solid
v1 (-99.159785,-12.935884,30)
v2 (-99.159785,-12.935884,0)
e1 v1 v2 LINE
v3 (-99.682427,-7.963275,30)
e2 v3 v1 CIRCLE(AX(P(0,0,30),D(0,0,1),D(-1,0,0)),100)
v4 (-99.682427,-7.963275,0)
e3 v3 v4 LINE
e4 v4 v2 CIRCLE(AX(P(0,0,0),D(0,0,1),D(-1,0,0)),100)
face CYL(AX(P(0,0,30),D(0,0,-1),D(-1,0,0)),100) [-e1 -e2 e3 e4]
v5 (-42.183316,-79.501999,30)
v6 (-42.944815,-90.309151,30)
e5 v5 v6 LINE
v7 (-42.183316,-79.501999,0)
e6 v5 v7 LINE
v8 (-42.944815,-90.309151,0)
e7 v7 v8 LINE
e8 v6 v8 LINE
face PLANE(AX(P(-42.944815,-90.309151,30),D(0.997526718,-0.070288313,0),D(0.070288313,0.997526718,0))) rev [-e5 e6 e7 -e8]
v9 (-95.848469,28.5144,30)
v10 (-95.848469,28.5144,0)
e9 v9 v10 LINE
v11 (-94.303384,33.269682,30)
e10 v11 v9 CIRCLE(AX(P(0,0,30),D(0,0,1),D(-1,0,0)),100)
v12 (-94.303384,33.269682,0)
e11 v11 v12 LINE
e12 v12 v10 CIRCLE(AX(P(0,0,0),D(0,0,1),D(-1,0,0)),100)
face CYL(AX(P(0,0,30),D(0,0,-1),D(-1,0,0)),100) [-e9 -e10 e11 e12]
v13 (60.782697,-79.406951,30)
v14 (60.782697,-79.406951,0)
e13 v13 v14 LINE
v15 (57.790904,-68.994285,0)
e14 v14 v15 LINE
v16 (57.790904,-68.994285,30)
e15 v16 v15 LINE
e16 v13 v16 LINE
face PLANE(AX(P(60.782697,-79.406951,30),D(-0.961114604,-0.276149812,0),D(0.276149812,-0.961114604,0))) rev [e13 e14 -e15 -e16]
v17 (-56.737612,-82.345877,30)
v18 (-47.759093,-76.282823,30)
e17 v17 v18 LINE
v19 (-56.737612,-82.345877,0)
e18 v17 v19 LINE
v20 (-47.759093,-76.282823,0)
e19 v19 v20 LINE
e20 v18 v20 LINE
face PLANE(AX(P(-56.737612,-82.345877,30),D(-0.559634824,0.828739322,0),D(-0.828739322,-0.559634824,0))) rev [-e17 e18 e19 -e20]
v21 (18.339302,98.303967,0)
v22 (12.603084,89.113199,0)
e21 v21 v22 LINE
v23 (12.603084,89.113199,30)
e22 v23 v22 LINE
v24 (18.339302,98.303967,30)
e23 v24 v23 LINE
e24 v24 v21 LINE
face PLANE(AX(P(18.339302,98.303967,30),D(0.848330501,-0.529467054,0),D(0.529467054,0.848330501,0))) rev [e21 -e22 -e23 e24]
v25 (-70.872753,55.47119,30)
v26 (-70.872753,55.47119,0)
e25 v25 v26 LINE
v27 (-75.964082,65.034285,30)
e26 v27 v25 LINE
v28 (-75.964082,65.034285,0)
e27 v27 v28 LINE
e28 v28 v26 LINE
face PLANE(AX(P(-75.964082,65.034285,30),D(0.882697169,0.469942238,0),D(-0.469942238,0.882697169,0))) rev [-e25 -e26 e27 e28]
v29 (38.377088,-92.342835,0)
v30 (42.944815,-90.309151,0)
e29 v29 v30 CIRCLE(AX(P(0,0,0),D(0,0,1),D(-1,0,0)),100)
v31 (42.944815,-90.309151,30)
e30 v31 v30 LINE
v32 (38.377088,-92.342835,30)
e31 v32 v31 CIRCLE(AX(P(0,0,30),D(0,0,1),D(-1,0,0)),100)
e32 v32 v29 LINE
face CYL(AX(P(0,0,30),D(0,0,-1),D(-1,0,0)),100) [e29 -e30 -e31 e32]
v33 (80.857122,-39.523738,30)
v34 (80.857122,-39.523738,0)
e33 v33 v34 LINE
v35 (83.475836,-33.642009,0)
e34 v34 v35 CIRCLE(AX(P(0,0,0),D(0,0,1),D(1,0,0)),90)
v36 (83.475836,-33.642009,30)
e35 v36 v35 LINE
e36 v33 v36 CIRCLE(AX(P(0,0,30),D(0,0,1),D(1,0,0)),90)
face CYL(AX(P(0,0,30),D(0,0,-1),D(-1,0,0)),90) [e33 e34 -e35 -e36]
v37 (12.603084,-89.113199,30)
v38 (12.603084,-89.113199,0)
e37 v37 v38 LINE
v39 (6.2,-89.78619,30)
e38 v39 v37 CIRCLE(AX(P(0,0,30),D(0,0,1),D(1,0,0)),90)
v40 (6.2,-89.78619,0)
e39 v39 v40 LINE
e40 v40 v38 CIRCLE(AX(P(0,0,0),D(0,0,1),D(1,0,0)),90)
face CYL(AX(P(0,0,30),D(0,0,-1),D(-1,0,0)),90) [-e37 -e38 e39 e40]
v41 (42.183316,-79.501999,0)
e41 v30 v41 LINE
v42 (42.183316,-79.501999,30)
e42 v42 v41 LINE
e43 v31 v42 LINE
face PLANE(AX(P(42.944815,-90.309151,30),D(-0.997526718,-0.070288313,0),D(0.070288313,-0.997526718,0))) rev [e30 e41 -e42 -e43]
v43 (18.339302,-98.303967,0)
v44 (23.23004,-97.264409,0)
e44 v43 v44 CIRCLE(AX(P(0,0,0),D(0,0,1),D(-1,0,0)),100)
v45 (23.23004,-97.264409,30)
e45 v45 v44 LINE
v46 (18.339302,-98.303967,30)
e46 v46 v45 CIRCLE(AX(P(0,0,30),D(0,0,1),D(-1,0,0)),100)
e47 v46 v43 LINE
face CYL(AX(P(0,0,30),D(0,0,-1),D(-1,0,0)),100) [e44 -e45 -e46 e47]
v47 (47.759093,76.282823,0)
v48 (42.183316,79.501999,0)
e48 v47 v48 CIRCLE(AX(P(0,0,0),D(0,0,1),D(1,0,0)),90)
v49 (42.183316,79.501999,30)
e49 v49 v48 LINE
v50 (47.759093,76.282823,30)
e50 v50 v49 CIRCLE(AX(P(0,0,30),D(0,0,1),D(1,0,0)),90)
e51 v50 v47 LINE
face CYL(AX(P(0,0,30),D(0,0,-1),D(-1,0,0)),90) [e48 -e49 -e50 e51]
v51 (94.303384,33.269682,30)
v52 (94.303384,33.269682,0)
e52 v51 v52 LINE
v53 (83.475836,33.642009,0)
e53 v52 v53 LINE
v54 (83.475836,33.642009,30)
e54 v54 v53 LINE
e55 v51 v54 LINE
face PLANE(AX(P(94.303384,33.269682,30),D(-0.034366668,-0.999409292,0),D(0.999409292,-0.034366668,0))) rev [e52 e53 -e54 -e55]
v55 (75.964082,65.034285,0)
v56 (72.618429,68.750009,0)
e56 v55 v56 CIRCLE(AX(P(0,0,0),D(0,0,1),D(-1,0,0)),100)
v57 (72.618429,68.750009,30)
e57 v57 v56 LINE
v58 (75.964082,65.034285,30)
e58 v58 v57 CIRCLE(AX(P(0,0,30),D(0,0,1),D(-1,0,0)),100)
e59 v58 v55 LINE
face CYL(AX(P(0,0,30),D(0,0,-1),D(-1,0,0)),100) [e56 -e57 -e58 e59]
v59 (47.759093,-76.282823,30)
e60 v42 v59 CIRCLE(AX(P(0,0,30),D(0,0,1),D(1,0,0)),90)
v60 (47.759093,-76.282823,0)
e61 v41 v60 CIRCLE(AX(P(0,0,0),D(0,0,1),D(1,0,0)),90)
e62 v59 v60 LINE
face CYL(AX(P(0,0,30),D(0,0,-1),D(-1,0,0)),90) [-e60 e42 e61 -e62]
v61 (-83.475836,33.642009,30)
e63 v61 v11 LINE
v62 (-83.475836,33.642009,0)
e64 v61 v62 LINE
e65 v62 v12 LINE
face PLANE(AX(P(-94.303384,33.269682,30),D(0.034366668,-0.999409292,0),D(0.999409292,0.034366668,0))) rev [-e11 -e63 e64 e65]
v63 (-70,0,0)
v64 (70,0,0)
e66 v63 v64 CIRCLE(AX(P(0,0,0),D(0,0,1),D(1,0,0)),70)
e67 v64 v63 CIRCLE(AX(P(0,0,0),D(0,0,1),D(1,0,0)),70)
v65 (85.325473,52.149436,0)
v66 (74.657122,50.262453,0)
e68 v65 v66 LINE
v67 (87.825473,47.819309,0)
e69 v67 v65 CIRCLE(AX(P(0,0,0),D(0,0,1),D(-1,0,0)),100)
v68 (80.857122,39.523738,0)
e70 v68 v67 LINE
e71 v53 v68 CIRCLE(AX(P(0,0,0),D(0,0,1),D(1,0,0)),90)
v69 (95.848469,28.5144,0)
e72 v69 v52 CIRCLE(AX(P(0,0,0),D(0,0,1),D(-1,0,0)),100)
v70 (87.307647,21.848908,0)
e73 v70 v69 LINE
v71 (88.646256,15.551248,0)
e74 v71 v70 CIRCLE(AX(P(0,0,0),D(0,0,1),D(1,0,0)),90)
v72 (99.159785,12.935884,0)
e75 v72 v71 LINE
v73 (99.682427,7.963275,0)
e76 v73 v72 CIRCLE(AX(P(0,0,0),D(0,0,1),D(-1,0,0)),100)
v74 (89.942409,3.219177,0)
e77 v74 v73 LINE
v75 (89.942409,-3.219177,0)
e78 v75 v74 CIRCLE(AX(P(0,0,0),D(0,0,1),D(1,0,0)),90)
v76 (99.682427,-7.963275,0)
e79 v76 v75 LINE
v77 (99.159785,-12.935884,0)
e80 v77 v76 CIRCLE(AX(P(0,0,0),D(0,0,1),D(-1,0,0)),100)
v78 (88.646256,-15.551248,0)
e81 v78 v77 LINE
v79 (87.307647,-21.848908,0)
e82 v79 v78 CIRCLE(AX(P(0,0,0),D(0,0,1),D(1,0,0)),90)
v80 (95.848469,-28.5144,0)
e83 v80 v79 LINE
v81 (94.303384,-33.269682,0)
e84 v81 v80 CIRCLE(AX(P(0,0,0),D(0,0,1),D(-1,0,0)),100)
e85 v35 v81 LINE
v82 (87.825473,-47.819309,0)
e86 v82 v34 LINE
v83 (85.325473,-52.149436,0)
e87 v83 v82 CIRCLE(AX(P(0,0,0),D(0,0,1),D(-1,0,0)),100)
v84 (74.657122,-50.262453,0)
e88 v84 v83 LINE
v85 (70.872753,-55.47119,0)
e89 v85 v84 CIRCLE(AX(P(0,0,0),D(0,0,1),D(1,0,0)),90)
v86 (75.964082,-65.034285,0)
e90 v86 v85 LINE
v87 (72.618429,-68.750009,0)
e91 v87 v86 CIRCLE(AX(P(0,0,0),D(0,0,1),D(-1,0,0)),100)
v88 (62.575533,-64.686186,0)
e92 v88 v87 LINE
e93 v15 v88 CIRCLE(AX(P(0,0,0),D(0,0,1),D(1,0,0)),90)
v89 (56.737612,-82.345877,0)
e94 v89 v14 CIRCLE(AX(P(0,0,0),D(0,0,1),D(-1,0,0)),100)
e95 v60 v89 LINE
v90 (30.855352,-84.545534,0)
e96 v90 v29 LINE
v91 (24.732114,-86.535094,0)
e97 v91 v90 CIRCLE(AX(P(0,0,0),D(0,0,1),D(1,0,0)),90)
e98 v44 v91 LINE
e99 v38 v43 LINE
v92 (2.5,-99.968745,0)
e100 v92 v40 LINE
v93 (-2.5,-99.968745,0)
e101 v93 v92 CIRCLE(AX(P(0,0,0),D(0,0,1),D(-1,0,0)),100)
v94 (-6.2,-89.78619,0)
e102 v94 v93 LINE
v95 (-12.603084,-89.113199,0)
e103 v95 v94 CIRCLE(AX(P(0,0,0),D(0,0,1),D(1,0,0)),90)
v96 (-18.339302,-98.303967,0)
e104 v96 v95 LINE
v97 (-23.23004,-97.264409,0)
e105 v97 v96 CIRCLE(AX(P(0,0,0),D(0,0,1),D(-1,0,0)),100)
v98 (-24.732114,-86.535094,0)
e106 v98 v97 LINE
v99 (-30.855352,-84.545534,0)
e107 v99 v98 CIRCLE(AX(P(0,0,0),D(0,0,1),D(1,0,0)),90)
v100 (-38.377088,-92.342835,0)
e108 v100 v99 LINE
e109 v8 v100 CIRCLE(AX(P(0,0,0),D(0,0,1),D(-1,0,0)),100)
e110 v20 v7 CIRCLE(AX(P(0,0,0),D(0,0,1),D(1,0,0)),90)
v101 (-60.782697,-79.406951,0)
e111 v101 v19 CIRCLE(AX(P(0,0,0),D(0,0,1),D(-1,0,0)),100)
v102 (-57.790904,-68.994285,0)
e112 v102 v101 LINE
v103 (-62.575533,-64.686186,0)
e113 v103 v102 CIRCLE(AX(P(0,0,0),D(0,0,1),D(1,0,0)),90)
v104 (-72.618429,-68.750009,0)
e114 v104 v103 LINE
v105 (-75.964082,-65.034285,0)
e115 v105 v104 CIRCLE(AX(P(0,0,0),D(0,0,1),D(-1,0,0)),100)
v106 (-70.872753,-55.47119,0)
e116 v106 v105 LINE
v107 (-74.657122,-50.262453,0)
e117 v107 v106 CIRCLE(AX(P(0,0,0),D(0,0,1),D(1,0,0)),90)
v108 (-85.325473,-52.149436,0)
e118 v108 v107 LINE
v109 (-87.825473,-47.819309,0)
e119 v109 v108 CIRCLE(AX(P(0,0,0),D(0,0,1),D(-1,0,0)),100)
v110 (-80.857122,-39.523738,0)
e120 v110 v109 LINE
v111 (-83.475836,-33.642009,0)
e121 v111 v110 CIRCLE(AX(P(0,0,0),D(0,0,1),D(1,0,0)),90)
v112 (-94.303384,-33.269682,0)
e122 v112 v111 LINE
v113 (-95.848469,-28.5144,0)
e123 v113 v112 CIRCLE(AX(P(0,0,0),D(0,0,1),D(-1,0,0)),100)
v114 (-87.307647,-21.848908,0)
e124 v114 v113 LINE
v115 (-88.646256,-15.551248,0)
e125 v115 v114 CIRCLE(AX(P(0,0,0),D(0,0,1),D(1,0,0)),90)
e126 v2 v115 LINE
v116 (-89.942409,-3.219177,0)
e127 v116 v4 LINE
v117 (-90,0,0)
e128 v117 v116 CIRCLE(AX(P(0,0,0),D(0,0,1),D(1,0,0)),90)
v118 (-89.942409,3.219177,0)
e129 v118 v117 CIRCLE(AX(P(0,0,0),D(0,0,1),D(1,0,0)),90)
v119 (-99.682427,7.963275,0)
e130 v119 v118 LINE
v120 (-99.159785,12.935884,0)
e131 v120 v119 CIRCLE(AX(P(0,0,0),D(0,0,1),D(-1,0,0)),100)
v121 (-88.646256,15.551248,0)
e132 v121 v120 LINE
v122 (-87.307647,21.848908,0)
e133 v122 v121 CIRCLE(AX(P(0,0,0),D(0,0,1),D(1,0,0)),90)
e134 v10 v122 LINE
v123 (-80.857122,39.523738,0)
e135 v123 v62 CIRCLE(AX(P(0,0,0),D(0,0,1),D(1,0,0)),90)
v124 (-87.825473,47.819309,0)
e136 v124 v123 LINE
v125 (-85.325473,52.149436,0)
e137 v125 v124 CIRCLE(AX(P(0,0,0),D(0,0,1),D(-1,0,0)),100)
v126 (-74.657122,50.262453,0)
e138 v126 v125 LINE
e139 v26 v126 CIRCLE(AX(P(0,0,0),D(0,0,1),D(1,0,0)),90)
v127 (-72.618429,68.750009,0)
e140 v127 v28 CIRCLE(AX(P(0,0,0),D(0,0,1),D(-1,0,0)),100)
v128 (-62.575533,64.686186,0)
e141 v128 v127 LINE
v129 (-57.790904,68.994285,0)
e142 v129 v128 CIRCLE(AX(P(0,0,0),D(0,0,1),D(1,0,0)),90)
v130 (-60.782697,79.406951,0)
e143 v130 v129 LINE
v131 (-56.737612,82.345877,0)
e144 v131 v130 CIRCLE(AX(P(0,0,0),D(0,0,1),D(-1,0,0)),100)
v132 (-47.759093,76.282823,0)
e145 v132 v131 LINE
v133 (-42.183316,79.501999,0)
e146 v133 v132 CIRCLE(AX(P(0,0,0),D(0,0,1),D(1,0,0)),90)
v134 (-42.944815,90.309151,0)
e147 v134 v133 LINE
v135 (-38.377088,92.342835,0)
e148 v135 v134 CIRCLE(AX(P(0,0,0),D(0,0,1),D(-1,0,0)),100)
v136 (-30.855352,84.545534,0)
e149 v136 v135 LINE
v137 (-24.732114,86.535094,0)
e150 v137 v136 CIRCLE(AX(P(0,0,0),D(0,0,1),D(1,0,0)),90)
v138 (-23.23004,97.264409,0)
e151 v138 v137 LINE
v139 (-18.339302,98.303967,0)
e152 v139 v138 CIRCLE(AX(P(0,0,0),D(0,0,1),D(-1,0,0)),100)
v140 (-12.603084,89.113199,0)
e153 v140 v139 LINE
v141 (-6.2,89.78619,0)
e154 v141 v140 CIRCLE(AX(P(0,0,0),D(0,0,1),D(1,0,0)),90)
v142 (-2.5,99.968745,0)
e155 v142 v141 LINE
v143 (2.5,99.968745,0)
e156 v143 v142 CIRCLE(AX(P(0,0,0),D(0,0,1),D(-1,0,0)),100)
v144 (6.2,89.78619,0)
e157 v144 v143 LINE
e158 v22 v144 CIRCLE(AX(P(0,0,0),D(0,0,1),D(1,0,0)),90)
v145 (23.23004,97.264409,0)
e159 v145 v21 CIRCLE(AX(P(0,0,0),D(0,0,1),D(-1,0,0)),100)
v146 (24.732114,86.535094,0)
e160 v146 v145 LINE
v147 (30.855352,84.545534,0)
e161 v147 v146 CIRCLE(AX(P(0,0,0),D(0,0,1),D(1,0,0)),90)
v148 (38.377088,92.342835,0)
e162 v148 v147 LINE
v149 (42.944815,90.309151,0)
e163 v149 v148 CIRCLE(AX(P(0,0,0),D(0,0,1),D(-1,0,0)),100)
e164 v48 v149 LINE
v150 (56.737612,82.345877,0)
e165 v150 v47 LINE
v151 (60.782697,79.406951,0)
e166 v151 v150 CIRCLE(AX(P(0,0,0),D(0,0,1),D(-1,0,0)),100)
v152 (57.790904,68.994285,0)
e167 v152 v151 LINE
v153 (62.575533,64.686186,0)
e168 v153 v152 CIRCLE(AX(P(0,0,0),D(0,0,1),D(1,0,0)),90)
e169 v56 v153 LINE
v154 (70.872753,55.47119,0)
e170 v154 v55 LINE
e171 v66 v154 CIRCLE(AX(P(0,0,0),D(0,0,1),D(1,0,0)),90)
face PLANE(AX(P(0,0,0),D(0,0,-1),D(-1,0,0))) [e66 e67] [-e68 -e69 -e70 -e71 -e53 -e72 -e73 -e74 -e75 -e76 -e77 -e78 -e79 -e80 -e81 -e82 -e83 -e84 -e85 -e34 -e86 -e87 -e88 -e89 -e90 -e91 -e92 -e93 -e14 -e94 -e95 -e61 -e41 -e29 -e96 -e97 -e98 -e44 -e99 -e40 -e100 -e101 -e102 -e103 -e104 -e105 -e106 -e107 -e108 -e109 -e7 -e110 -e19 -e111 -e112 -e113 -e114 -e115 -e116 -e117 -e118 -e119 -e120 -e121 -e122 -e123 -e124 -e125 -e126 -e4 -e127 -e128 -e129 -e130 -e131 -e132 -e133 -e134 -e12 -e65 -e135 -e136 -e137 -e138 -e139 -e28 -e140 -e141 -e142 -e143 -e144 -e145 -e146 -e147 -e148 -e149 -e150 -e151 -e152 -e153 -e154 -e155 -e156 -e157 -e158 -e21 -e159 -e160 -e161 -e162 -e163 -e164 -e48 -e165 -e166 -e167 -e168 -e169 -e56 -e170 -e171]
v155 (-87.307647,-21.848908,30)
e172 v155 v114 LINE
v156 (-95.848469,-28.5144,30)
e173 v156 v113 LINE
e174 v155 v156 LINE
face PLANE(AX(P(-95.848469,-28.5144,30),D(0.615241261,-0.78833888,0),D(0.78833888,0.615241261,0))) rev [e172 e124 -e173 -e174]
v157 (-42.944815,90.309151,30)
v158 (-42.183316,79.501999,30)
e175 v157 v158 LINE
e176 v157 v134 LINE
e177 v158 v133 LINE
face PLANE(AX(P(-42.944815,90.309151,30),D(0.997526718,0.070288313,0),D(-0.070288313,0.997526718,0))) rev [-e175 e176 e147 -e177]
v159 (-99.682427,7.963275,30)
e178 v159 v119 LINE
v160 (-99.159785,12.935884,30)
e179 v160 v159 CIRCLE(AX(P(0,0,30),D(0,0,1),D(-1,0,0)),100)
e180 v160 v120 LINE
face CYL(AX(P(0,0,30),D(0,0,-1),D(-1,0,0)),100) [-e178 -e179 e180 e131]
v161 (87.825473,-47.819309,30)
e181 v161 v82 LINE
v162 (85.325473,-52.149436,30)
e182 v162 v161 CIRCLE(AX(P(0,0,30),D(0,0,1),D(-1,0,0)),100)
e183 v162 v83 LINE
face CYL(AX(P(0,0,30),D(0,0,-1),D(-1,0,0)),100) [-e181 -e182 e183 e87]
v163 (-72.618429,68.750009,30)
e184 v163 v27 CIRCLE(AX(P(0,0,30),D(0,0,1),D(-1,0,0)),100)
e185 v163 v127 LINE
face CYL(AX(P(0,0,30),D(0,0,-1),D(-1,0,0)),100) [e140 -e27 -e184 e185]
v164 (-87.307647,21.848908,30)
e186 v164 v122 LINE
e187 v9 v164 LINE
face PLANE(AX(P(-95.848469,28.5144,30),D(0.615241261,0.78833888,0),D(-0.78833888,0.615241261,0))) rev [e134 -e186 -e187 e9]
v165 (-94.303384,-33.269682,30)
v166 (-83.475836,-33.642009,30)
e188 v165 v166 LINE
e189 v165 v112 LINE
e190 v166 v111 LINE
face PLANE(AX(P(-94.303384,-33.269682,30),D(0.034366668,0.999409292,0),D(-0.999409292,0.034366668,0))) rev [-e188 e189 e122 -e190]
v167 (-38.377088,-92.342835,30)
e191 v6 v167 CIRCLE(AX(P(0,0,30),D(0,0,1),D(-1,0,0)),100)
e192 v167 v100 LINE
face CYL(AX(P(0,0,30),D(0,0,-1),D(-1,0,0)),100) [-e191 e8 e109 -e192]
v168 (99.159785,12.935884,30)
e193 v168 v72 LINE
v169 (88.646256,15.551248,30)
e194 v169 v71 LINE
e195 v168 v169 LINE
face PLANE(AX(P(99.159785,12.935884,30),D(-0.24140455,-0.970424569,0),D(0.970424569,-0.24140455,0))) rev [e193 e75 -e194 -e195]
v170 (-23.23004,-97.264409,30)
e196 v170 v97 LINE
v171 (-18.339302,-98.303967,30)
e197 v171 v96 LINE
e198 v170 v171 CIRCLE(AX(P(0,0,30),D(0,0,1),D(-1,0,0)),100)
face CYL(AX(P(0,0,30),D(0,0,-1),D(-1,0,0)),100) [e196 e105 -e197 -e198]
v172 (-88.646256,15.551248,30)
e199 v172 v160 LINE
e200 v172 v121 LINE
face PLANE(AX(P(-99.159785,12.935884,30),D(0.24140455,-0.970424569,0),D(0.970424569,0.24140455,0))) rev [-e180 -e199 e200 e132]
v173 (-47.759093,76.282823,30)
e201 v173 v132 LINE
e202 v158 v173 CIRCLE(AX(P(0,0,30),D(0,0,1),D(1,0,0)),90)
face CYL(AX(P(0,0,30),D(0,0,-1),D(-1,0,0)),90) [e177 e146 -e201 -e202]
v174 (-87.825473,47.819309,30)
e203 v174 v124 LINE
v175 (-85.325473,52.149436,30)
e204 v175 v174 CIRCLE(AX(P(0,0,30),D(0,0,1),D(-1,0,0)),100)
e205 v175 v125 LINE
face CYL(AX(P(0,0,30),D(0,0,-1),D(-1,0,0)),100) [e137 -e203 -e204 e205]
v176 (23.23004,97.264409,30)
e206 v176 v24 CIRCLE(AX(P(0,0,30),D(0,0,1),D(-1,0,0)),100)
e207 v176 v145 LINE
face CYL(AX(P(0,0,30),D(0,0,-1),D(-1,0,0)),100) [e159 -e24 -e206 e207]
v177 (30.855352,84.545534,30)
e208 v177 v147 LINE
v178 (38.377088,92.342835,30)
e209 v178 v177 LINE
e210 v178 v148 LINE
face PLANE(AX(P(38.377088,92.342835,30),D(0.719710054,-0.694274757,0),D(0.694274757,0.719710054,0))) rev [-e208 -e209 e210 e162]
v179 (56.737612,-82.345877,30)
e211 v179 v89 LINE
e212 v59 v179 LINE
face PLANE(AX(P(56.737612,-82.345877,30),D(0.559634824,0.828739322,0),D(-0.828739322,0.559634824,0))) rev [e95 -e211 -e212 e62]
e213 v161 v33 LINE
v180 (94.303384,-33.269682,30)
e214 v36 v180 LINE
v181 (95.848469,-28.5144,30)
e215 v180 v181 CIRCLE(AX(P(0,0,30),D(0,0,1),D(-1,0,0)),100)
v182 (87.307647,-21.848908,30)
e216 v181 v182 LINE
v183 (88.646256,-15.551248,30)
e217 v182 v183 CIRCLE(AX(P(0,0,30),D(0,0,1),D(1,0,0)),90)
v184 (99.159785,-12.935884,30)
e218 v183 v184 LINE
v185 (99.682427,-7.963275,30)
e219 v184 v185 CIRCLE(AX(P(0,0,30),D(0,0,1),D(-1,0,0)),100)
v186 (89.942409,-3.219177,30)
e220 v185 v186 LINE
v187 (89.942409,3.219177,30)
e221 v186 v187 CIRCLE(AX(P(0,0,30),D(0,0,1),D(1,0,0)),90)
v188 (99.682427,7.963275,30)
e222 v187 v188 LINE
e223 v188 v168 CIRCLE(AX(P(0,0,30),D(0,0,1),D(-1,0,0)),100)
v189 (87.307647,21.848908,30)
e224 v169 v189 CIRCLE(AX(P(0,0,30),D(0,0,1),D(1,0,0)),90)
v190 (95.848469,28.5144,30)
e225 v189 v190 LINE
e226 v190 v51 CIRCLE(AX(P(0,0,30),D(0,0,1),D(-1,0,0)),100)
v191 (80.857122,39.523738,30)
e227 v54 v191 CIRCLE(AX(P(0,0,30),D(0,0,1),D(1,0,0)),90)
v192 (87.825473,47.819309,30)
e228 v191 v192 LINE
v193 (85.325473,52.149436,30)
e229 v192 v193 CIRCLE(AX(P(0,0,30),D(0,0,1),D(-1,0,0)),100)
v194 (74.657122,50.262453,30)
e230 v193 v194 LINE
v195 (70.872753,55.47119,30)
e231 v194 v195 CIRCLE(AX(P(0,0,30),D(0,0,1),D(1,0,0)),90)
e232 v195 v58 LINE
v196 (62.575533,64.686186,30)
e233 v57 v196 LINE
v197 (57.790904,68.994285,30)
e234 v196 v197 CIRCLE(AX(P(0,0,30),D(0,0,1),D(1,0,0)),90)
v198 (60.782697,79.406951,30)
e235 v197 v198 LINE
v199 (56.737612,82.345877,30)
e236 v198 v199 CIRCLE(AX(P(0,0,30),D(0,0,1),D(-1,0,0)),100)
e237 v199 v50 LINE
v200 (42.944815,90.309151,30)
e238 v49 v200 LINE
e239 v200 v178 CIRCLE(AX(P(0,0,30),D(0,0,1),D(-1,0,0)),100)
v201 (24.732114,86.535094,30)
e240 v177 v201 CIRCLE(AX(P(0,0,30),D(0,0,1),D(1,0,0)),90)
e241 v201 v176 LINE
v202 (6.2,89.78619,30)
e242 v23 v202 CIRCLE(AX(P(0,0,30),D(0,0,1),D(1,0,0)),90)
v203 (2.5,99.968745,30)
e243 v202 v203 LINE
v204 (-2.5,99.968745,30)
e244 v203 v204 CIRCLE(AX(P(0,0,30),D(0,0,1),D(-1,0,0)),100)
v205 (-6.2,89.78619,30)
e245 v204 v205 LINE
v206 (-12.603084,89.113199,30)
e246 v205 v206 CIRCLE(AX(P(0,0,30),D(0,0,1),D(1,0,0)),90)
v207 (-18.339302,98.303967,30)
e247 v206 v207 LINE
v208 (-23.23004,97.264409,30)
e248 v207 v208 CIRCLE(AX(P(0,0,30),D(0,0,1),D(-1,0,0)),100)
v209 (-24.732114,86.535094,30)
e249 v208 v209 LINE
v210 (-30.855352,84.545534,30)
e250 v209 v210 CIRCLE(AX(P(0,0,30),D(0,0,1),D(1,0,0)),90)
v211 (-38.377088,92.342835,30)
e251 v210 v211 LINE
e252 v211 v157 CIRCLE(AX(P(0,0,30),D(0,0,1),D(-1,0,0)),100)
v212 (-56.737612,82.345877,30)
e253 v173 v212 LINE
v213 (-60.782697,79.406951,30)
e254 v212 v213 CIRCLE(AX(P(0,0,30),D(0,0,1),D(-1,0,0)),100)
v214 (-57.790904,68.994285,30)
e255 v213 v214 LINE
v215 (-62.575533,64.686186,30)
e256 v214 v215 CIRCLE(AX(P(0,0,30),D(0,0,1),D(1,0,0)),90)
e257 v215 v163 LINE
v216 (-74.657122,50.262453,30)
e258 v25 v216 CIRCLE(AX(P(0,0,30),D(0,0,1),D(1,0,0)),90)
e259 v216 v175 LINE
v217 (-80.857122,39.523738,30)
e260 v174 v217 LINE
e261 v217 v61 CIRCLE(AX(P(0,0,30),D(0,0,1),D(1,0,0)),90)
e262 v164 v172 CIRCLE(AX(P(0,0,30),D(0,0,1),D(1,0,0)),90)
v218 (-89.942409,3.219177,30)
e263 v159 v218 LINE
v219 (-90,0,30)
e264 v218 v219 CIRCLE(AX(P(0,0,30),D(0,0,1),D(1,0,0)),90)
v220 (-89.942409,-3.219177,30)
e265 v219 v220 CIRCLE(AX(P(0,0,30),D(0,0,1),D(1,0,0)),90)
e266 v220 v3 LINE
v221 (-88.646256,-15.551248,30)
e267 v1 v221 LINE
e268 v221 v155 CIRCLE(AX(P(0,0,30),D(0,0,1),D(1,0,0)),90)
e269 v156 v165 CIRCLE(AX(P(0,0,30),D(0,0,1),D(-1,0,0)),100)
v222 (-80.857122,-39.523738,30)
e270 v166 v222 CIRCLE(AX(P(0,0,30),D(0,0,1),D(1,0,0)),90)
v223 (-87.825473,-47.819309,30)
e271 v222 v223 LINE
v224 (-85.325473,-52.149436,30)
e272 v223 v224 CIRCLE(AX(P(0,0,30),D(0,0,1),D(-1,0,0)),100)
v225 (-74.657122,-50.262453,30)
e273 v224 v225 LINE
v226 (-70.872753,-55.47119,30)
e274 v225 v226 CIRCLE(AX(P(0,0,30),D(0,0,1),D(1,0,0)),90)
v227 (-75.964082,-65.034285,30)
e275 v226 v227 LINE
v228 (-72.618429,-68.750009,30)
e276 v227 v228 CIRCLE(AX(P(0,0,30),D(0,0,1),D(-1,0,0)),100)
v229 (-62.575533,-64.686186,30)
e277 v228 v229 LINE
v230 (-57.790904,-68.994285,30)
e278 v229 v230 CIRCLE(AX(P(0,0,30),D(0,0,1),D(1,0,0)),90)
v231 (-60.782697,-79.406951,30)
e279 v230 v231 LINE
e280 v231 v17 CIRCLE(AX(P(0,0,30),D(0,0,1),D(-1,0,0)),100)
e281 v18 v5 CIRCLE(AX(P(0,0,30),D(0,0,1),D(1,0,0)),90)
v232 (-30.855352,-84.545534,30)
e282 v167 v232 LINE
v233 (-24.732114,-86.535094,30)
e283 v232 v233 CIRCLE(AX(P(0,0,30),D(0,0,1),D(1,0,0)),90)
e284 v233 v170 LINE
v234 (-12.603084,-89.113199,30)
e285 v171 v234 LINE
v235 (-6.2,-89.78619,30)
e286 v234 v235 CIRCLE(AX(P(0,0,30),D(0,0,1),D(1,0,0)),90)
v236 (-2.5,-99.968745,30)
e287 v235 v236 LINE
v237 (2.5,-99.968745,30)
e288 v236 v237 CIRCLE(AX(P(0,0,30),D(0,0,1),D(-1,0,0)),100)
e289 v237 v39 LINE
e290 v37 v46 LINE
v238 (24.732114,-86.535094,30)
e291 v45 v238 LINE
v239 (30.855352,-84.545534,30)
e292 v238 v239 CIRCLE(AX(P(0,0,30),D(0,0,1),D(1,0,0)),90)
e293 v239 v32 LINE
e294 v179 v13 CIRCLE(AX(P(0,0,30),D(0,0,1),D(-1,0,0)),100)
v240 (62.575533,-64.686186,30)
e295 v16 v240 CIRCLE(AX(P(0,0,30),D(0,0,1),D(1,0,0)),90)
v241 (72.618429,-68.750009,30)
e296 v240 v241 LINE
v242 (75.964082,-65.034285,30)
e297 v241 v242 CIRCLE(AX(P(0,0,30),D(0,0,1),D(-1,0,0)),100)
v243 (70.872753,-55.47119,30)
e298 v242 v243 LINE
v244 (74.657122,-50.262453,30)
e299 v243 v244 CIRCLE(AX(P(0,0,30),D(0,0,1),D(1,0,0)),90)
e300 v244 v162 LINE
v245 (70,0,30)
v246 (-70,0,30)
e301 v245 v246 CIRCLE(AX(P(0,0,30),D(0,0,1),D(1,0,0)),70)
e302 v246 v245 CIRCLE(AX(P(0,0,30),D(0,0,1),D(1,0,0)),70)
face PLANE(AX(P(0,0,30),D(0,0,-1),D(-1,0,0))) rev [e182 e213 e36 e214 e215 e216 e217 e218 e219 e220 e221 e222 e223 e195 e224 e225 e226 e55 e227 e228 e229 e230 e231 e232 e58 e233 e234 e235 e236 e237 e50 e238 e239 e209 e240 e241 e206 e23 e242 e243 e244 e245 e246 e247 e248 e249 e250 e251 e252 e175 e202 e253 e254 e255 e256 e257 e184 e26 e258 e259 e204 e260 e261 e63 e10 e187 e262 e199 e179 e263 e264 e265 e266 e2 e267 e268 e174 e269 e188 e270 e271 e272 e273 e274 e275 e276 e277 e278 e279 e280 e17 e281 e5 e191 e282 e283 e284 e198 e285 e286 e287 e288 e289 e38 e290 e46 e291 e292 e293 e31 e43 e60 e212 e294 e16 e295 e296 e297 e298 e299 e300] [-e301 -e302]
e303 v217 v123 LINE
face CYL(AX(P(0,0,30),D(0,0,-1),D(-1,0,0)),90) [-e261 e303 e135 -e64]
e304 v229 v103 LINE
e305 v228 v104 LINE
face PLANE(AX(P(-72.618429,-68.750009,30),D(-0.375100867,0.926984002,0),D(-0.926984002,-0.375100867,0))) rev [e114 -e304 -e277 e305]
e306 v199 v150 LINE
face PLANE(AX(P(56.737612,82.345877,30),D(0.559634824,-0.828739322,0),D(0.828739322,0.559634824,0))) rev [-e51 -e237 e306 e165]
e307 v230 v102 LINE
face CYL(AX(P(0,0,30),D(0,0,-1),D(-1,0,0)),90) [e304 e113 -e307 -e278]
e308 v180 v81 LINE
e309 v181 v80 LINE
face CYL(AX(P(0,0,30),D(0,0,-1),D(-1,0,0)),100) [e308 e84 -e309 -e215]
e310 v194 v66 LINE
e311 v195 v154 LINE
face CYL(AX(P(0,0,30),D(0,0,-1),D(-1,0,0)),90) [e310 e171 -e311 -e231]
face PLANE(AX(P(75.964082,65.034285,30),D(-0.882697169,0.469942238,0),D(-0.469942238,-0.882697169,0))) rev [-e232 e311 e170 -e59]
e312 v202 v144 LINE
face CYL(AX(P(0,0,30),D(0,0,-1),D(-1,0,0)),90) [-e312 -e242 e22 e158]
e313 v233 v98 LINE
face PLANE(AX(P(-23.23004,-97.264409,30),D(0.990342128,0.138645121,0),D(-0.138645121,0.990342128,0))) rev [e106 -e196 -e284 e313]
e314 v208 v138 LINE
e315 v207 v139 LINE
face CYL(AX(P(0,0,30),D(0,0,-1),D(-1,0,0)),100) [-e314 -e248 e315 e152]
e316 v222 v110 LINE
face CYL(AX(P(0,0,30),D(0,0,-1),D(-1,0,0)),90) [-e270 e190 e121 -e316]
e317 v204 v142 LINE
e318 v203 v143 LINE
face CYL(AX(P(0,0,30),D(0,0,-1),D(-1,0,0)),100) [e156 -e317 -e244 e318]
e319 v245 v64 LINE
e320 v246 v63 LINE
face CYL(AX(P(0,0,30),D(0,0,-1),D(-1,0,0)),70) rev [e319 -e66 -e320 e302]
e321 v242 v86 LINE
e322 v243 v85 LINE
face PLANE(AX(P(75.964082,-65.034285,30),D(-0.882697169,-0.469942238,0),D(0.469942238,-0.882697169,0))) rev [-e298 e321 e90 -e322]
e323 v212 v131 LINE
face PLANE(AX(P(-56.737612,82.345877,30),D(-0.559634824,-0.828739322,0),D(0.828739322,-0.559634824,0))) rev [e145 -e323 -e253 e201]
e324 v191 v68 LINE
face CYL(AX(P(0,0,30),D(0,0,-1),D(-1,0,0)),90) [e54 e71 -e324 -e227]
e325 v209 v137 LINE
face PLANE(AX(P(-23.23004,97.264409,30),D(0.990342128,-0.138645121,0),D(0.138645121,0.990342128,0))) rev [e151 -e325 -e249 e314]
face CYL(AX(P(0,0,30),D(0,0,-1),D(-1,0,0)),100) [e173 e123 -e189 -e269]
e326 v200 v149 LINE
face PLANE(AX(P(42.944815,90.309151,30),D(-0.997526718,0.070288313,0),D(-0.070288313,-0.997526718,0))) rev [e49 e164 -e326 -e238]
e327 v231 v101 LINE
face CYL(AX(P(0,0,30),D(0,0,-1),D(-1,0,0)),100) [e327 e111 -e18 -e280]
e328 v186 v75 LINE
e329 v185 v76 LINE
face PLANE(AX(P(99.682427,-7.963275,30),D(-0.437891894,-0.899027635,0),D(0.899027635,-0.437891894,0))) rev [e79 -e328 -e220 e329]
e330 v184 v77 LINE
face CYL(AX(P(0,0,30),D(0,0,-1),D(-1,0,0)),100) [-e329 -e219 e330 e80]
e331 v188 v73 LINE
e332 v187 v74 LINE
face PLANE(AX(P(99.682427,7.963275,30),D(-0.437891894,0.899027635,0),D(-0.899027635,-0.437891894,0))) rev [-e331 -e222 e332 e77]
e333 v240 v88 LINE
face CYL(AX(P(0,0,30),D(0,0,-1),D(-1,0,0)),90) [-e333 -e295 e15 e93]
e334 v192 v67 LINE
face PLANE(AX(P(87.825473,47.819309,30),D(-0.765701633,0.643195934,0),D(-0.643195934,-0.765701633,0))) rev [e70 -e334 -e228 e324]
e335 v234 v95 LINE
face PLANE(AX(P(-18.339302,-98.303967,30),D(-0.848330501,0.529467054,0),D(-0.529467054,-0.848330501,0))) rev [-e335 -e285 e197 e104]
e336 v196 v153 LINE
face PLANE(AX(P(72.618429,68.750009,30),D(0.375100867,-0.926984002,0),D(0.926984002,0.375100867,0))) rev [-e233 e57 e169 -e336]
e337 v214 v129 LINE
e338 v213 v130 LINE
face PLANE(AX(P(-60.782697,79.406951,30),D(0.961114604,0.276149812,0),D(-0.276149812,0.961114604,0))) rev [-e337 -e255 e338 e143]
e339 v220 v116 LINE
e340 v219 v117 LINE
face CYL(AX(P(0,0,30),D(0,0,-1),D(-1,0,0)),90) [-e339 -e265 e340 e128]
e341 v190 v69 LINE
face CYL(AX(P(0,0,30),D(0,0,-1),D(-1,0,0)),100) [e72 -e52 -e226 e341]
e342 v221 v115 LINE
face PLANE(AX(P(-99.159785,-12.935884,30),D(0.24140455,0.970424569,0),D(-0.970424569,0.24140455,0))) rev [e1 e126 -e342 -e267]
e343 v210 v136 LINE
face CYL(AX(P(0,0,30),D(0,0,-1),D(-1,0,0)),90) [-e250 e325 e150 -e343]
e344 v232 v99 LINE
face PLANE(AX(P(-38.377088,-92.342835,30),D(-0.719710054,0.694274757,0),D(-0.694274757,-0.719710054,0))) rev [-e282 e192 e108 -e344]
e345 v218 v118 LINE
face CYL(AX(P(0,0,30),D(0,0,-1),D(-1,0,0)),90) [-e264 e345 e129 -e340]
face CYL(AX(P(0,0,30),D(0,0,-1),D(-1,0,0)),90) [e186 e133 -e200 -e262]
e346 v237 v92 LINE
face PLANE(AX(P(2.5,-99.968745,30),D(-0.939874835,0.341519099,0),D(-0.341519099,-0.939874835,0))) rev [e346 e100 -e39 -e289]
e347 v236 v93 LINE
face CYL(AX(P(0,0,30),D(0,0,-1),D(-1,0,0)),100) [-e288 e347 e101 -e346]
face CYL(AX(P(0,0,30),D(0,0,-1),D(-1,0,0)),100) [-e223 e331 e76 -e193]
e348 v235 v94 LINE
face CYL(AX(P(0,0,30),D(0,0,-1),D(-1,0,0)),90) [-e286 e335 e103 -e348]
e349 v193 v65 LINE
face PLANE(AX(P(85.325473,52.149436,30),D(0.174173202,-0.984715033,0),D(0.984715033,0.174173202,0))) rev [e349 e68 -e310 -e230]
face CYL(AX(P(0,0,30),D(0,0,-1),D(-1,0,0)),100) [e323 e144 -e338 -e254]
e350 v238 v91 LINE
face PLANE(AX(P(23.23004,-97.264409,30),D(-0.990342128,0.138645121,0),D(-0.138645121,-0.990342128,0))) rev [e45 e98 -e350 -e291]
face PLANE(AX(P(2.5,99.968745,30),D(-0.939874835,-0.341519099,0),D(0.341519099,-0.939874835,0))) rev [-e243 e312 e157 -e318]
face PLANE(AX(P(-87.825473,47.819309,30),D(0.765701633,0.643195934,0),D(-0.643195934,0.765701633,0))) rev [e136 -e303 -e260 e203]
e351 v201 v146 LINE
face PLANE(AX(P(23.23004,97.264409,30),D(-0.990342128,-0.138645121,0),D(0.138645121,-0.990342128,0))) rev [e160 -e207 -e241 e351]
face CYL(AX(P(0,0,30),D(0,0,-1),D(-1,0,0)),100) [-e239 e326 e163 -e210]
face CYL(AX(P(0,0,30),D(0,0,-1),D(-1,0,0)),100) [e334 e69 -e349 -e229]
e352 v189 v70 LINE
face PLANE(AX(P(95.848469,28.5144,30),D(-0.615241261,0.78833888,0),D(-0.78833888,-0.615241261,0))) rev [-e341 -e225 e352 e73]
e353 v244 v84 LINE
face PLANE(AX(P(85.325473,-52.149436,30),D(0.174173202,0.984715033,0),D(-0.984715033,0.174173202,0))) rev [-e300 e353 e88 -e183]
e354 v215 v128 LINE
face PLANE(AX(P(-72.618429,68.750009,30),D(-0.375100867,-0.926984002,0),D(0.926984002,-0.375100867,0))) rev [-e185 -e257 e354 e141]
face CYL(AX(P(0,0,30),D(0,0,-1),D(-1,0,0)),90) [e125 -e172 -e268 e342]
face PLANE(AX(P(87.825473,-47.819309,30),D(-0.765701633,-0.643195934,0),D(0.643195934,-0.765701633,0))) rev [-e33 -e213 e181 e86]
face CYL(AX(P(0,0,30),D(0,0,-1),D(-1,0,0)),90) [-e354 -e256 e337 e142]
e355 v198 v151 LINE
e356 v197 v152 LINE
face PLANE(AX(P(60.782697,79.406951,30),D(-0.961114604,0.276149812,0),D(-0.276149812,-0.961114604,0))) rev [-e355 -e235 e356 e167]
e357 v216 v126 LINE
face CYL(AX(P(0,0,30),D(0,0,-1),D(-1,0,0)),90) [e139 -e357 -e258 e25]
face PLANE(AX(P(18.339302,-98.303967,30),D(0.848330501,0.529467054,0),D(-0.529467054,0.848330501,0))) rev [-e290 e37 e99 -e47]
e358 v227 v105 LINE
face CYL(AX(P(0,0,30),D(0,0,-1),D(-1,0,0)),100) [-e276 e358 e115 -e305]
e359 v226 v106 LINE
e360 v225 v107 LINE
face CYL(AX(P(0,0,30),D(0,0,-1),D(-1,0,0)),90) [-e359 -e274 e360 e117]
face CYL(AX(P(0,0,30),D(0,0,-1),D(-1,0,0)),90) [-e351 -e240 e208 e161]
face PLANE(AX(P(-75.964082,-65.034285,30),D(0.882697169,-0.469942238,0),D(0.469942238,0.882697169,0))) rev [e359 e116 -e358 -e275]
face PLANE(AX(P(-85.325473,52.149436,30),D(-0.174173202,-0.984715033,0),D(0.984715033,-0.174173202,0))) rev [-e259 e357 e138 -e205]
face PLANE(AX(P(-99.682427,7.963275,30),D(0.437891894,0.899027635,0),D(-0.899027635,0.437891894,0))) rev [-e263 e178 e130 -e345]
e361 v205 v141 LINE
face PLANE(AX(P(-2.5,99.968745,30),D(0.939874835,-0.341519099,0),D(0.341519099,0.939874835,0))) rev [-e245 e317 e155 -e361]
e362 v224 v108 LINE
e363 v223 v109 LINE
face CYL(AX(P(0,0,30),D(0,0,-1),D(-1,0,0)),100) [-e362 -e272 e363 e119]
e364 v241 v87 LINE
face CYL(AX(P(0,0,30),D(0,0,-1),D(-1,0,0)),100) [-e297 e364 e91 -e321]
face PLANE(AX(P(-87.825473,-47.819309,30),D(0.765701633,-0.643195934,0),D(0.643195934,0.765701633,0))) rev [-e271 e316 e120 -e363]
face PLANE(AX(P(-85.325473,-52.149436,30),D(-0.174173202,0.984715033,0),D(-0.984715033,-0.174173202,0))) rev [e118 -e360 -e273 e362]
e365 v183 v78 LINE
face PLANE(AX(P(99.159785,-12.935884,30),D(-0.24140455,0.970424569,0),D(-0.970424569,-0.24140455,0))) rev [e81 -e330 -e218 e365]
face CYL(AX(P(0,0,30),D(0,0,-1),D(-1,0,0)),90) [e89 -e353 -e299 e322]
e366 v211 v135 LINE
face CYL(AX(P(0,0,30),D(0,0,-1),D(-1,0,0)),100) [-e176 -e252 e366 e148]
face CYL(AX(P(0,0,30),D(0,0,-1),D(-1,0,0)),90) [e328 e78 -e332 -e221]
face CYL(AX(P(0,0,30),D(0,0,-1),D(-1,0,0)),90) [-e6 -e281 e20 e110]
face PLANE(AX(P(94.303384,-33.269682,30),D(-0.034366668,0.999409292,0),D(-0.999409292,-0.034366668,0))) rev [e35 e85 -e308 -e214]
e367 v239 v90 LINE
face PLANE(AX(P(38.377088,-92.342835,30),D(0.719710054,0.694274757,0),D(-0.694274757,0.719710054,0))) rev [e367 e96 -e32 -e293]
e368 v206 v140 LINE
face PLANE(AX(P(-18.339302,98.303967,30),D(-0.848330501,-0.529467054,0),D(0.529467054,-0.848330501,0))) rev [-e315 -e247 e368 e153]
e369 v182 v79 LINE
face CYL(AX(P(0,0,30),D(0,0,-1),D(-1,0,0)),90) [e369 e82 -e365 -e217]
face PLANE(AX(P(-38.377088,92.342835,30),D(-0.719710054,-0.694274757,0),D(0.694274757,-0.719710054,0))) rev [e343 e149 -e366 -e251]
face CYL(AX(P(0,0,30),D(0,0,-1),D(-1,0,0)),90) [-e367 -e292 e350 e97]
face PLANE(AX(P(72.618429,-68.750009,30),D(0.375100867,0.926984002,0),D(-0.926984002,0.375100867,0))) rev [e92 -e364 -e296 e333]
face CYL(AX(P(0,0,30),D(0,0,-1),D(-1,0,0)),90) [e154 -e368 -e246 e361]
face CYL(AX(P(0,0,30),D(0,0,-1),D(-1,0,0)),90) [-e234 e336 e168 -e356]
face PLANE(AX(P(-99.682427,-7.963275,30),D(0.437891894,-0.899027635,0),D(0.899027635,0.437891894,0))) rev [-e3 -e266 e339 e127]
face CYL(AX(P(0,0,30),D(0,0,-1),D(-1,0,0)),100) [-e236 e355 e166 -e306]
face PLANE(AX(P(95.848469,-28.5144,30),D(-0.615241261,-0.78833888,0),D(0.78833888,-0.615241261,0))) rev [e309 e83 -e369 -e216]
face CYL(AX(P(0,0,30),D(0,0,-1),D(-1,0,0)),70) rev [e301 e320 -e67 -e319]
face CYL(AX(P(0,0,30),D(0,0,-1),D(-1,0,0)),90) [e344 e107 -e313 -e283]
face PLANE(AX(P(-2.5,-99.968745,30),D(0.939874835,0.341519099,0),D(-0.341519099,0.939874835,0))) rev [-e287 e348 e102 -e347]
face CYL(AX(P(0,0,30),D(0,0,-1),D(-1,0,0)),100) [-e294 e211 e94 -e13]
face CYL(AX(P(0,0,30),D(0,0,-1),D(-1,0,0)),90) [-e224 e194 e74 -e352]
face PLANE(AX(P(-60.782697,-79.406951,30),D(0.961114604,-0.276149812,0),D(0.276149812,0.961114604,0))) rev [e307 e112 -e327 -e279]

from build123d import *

# Parameters (mm, degrees)
SKETCH1_R           = 70
BOSS_EXTRUDE1_DEPTH = 30


with BuildPart() as part:
    # Sketch1 → Boss-Extrude1 (new body)
    with BuildSketch(Plane.XY):
        with BuildLine():
            Line((-2.5, 99.968745116), (-6.2, 89.786190475))
            ThreePointArc((-6.2, 89.786190475), (-9.407561694, 89.506970583), (-12.603083549, 89.113199275))
            Line((-12.603083549, 89.113199275), (-18.339301824, 98.30396741))
            ThreePointArc((-18.339301824, 98.30396741), (-20.791169082, 97.814760073), (-23.230039828, 97.264408956))
            Line((-23.230039828, 97.264408956), (-24.732113798, 86.535094309))
            ThreePointArc((-24.732113798, 86.535094309), (-27.811529494, 85.595086467), (-30.855351871, 84.545533654))
            Line((-30.855351871, 84.545533654), (-38.377088157, 92.342834614))
            ThreePointArc((-38.377088157, 92.342834614), (-40.673664308, 91.354545764), (-42.944815445, 90.309151399))
            Line((-42.944815445, 90.309151399), (-42.183315546, 79.50199928))
            ThreePointArc((-42.183315546, 79.50199928), (-45, 77.942286341), (-47.759093256, 76.282822519))
            Line((-47.759093256, 76.282822519), (-56.737611583, 82.345876836))
            ThreePointArc((-56.737611583, 82.345876836), (-58.778525229, 80.901699437), (-60.782696555, 79.406950574))
            Line((-60.782696555, 79.406950574), (-57.790903986, 68.99428539))
            ThreePointArc((-57.790903986, 68.99428539), (-60.221754572, 66.883034293), (-62.575533091, 64.686185993))
            Line((-62.575533091, 64.686185993), (-72.618429126, 68.7500091))
            ThreePointArc((-72.618429126, 68.7500091), (-74.314482548, 66.913060636), (-75.964082158, 65.034284972))
            Line((-75.964082158, 65.034284972), (-70.87275261, 55.471190157))
            ThreePointArc((-70.87275261, 55.471190157), (-72.811529494, 52.900672706), (-74.65712186, 50.262452741))
            Line((-74.65712186, 50.262452741), (-85.325472855, 52.149436067))
            ThreePointArc((-85.325472855, 52.149436067), (-86.602540378, 50), (-87.825472855, 47.819309048))
            Line((-87.825472855, 47.819309048), (-80.85712186, 39.523737734))
            ThreePointArc((-80.85712186, 39.523737734), (-82.219091188, 36.606297877), (-83.475836159, 33.642009118))
            Line((-83.475836159, 33.642009118), (-94.303383982, 33.269682438))
            ThreePointArc((-94.303383982, 33.269682438), (-95.10565163, 30.901699437), (-95.848468954, 28.514399856))
            Line((-95.848468954, 28.514399856), (-87.30764689, 21.848908316))
            ThreePointArc((-87.30764689, 21.848908316), (-88.033284066, 18.712052174), (-88.646255857, 15.551248264))
            Line((-88.646255857, 15.551248264), (-99.159784712, 12.93588404))
            ThreePointArc((-99.159784712, 12.93588404), (-99.452189537, 10.452846327), (-99.682427028, 7.963274563))
            Line((-99.682427028, 7.963274563), (-89.942408801, 3.219176762))
            ThreePointArc((-89.942408801, 3.219176762), (-90, 0), (-89.942408801, -3.219176762))
            Line((-89.942408801, -3.219176762), (-99.682427028, -7.963274563))
            ThreePointArc((-99.682427028, -7.963274563), (-99.452189537, -10.452846327), (-99.159784712, -12.93588404))
            Line((-99.159784712, -12.93588404), (-88.646255857, -15.551248264))
            ThreePointArc((-88.646255857, -15.551248264), (-88.033284066, -18.712052174), (-87.30764689, -21.848908316))
            Line((-87.30764689, -21.848908316), (-95.848468954, -28.514399856))
            ThreePointArc((-95.848468954, -28.514399856), (-95.10565163, -30.901699437), (-94.303383982, -33.269682438))
            Line((-94.303383982, -33.269682438), (-83.475836159, -33.642009118))
            ThreePointArc((-83.475836159, -33.642009118), (-82.219091188, -36.606297877), (-80.85712186, -39.523737734))
            Line((-80.85712186, -39.523737734), (-87.825472855, -47.819309048))
            ThreePointArc((-87.825472855, -47.819309048), (-86.602540378, -50), (-85.325472855, -52.149436067))
            Line((-85.325472855, -52.149436067), (-74.65712186, -50.262452741))
            ThreePointArc((-74.65712186, -50.262452741), (-72.811529494, -52.900672706), (-70.87275261, -55.471190157))
            Line((-70.87275261, -55.471190157), (-75.964082158, -65.034284972))
            ThreePointArc((-75.964082158, -65.034284972), (-74.314482548, -66.913060636), (-72.618429126, -68.7500091))
            Line((-72.618429126, -68.7500091), (-62.575533091, -64.686185993))
            ThreePointArc((-62.575533091, -64.686185993), (-60.221754572, -66.883034293), (-57.790903986, -68.99428539))
            Line((-57.790903986, -68.99428539), (-60.782696555, -79.406950574))
            ThreePointArc((-60.782696555, -79.406950574), (-58.778525229, -80.901699437), (-56.737611583, -82.345876836))
            Line((-56.737611583, -82.345876836), (-47.759093256, -76.282822519))
            ThreePointArc((-47.759093256, -76.282822519), (-45, -77.942286341), (-42.183315546, -79.50199928))
            Line((-42.183315546, -79.50199928), (-42.944815445, -90.309151399))
            ThreePointArc((-42.944815445, -90.309151399), (-40.673664308, -91.354545764), (-38.377088157, -92.342834614))
            Line((-38.377088157, -92.342834614), (-30.855351871, -84.545533654))
            ThreePointArc((-30.855351871, -84.545533654), (-27.811529494, -85.595086467), (-24.732113798, -86.535094309))
            Line((-24.732113798, -86.535094309), (-23.230039828, -97.264408956))
            ThreePointArc((-23.230039828, -97.264408956), (-20.791169082, -97.814760073), (-18.339301824, -98.30396741))
            Line((-18.339301824, -98.30396741), (-12.603083549, -89.113199275))
            ThreePointArc((-12.603083549, -89.113199275), (-9.407561694, -89.506970583), (-6.2, -89.786190475))
            Line((-6.2, -89.786190475), (-2.5, -99.968745116))
            ThreePointArc((-2.5, -99.968745116), (0, -100), (2.5, -99.968745116))
            Line((2.5, -99.968745116), (6.2, -89.786190475))
            ThreePointArc((6.2, -89.786190475), (9.407561694, -89.506970583), (12.603083549, -89.113199275))
            Line((12.603083549, -89.113199275), (18.339301824, -98.30396741))
            ThreePointArc((18.339301824, -98.30396741), (20.791169082, -97.814760073), (23.230039828, -97.264408956))
            Line((23.230039828, -97.264408956), (24.732113798, -86.535094309))
            ThreePointArc((24.732113798, -86.535094309), (27.811529494, -85.595086467), (30.855351871, -84.545533654))
            Line((30.855351871, -84.545533654), (38.377088157, -92.342834614))
            ThreePointArc((38.377088157, -92.342834614), (40.673664308, -91.354545764), (42.944815445, -90.309151399))
            Line((42.944815445, -90.309151399), (42.183315546, -79.50199928))
            ThreePointArc((42.183315546, -79.50199928), (45, -77.942286341), (47.759093256, -76.282822519))
            Line((47.759093256, -76.282822519), (56.737611583, -82.345876836))
            ThreePointArc((56.737611583, -82.345876836), (58.778525229, -80.901699437), (60.782696555, -79.406950574))
            Line((60.782696555, -79.406950574), (57.790903986, -68.99428539))
            ThreePointArc((57.790903986, -68.99428539), (60.221754572, -66.883034293), (62.575533091, -64.686185993))
            Line((62.575533091, -64.686185993), (72.618429126, -68.7500091))
            ThreePointArc((72.618429126, -68.7500091), (74.314482548, -66.913060636), (75.964082158, -65.034284972))
            Line((75.964082158, -65.034284972), (70.87275261, -55.471190157))
            ThreePointArc((70.87275261, -55.471190157), (72.811529494, -52.900672706), (74.65712186, -50.262452741))
            Line((74.65712186, -50.262452741), (85.325472855, -52.149436067))
            ThreePointArc((85.325472855, -52.149436067), (86.602540378, -50), (87.825472855, -47.819309048))
            Line((87.825472855, -47.819309048), (80.85712186, -39.523737734))
            ThreePointArc((80.85712186, -39.523737734), (82.219091188, -36.606297877), (83.475836159, -33.642009118))
            Line((83.475836159, -33.642009118), (94.303383982, -33.269682438))
            ThreePointArc((94.303383982, -33.269682438), (95.10565163, -30.901699437), (95.848468954, -28.514399856))
            Line((95.848468954, -28.514399856), (87.30764689, -21.848908316))
            ThreePointArc((87.30764689, -21.848908316), (88.033284066, -18.712052174), (88.646255857, -15.551248264))
            Line((88.646255857, -15.551248264), (99.159784712, -12.93588404))
            ThreePointArc((99.159784712, -12.93588404), (99.452189537, -10.452846327), (99.682427028, -7.963274563))
            Line((99.682427028, -7.963274563), (89.942408801, -3.219176762))
            ThreePointArc((89.942408801, -3.219176762), (90, 0), (89.942408801, 3.219176762))
            Line((89.942408801, 3.219176762), (99.682427028, 7.963274563))
            ThreePointArc((99.682427028, 7.963274563), (99.452189537, 10.452846327), (99.159784712, 12.93588404))
            Line((99.159784712, 12.93588404), (88.646255857, 15.551248264))
            ThreePointArc((88.646255857, 15.551248264), (88.033284066, 18.712052174), (87.30764689, 21.848908316))
            Line((87.30764689, 21.848908316), (95.848468954, 28.514399856))
            ThreePointArc((95.848468954, 28.514399856), (95.10565163, 30.901699437), (94.303383982, 33.269682438))
            Line((94.303383982, 33.269682438), (83.475836159, 33.642009118))
            ThreePointArc((83.475836159, 33.642009118), (82.219091188, 36.606297877), (80.85712186, 39.523737734))
            Line((80.85712186, 39.523737734), (87.825472855, 47.819309048))
            ThreePointArc((87.825472855, 47.819309048), (86.602540378, 50), (85.325472855, 52.149436067))
            Line((85.325472855, 52.149436067), (74.65712186, 50.262452741))
            ThreePointArc((74.65712186, 50.262452741), (72.811529494, 52.900672706), (70.87275261, 55.471190157))
            Line((70.87275261, 55.471190157), (75.964082158, 65.034284972))
            ThreePointArc((75.964082158, 65.034284972), (74.314482548, 66.913060636), (72.618429126, 68.7500091))
            Line((72.618429126, 68.7500091), (62.575533091, 64.686185993))
            ThreePointArc((62.575533091, 64.686185993), (60.221754572, 66.883034293), (57.790903986, 68.99428539))
            Line((57.790903986, 68.99428539), (60.782696555, 79.406950574))
            ThreePointArc((60.782696555, 79.406950574), (58.778525229, 80.901699437), (56.737611583, 82.345876836))
            Line((56.737611583, 82.345876836), (47.759093256, 76.282822519))
            ThreePointArc((47.759093256, 76.282822519), (45, 77.942286341), (42.183315546, 79.50199928))
            Line((42.183315546, 79.50199928), (42.944815445, 90.309151399))
            ThreePointArc((42.944815445, 90.309151399), (40.673664308, 91.354545764), (38.377088157, 92.342834614))
            Line((38.377088157, 92.342834614), (30.855351871, 84.545533654))
            ThreePointArc((30.855351871, 84.545533654), (27.811529494, 85.595086467), (24.732113798, 86.535094309))
            Line((24.732113798, 86.535094309), (23.230039828, 97.264408956))
            ThreePointArc((23.230039828, 97.264408956), (20.791169082, 97.814760073), (18.339301824, 98.30396741))
            Line((18.339301824, 98.30396741), (12.603083549, 89.113199275))
            ThreePointArc((12.603083549, 89.113199275), (9.407561694, 89.506970583), (6.2, 89.786190475))
            Line((6.2, 89.786190475), (2.5, 99.968745116))
            ThreePointArc((2.5, 99.968745116), (0, 100), (-2.5, 99.968745116))
        make_face()
        Circle(SKETCH1_R, mode=Mode.SUBTRACT)
    extrude(amount=BOSS_EXTRUDE1_DEPTH)


solid = part.part
